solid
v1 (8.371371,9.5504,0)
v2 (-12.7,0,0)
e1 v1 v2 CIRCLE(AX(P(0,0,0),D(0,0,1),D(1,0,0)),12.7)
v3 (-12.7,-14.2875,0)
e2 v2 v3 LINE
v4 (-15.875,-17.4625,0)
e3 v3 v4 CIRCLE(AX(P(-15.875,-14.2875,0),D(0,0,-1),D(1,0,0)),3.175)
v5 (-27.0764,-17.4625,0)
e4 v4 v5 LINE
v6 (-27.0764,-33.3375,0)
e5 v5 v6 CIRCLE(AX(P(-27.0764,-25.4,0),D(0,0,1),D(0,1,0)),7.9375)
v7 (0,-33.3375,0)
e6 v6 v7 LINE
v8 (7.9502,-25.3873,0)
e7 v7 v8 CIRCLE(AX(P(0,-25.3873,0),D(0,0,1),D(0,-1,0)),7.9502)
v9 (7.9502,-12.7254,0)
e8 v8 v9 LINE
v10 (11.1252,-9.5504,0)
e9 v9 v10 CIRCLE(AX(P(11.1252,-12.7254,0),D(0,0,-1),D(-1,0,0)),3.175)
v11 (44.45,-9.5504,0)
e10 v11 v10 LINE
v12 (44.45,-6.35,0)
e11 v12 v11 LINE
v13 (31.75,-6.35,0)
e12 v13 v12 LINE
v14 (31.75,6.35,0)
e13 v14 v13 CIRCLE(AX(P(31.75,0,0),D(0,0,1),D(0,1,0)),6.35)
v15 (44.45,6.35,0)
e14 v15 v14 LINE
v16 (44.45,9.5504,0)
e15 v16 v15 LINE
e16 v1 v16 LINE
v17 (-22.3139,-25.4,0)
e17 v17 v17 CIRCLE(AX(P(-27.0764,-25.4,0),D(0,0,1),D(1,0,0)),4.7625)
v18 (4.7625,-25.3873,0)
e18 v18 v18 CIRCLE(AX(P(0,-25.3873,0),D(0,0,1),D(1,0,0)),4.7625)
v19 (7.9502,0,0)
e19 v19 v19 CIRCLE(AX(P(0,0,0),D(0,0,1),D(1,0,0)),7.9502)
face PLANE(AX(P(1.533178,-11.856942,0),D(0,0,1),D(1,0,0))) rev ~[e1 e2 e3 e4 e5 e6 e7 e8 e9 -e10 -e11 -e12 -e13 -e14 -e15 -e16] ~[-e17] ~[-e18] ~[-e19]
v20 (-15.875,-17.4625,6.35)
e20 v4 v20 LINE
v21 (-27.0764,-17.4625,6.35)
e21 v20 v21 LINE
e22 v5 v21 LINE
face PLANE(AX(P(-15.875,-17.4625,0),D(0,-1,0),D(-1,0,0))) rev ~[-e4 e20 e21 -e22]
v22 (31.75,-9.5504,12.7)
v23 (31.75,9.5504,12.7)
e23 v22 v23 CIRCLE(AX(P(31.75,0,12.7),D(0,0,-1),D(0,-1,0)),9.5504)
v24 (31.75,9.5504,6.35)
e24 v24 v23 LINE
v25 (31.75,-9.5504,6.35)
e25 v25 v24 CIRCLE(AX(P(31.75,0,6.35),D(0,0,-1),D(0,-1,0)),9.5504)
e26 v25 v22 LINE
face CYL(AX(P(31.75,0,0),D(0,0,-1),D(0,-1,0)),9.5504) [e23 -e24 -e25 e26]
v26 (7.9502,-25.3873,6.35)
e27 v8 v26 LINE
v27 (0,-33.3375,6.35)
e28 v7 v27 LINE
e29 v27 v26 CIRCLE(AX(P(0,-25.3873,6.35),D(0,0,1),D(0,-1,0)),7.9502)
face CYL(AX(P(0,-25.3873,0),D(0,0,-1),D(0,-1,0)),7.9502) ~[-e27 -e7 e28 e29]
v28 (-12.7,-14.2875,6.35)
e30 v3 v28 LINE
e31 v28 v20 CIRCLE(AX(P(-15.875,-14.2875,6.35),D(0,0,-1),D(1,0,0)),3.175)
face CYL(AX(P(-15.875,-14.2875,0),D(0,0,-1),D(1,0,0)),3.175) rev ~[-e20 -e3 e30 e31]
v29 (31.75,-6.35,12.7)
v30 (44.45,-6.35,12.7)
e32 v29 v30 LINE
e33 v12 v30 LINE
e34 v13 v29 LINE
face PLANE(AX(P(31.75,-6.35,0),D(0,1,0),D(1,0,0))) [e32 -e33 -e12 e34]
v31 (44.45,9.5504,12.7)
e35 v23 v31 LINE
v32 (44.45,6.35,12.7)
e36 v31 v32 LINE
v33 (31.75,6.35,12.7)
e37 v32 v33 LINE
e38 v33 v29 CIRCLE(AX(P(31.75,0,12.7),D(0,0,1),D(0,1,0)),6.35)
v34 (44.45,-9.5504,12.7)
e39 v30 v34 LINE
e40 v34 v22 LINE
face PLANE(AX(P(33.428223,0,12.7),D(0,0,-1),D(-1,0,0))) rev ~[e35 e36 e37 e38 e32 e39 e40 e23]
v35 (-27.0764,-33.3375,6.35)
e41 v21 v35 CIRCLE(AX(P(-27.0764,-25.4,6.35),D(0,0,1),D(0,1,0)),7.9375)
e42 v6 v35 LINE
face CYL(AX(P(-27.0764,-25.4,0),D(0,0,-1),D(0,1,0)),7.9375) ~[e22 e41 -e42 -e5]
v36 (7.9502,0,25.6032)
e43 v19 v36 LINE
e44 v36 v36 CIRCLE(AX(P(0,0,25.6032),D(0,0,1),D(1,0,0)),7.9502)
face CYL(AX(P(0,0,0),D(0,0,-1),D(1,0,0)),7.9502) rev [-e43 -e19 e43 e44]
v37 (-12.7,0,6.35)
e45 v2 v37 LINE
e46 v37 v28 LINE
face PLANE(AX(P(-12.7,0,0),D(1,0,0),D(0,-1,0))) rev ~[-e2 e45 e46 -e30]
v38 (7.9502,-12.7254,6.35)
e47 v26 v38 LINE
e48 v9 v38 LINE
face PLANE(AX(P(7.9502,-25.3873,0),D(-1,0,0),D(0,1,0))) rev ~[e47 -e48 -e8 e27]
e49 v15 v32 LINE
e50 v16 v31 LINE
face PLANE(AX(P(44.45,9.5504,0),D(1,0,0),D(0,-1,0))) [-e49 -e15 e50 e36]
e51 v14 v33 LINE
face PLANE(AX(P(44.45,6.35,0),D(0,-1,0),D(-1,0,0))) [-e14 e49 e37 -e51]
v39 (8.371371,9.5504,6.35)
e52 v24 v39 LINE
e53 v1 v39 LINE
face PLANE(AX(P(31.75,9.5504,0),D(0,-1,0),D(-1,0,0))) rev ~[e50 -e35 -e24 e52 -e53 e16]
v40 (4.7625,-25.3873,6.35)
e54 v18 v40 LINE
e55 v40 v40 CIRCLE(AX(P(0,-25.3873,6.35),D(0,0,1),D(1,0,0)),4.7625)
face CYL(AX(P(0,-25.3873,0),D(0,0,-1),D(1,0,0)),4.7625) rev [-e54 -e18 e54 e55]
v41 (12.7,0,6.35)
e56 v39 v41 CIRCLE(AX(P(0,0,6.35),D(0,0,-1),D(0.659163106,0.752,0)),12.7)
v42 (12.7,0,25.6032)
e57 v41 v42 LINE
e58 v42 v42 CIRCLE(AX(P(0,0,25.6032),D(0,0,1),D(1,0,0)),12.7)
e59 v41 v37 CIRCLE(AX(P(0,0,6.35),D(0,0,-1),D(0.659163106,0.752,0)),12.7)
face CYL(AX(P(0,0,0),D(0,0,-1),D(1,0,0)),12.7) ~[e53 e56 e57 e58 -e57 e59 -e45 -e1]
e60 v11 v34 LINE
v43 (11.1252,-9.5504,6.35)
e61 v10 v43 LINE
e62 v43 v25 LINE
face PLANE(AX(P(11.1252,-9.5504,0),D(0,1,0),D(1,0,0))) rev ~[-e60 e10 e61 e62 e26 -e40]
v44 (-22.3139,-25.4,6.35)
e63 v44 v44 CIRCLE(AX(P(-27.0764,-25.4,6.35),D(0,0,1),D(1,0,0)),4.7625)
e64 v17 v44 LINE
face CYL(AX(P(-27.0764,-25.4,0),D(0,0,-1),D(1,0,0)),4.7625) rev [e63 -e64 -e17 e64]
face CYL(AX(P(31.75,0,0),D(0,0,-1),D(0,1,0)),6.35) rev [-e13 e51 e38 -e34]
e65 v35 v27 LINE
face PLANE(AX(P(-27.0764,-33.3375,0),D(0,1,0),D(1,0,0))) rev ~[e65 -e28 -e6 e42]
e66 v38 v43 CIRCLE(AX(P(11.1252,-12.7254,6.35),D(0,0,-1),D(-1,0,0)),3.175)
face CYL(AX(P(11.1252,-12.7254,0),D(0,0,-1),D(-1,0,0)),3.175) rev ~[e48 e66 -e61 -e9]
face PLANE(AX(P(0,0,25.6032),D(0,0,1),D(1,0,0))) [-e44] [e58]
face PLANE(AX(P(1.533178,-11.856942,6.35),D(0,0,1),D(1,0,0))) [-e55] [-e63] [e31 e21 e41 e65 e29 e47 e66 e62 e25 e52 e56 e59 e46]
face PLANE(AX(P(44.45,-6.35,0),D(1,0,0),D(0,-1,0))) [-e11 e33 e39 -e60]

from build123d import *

# Parameters (mm, degrees)
HUB_TUBE_SKETCH_R   = 12.7
HUB_TUBE_SKETCH_R_2 = 7.9502
HUB_TUBE_DEPTH      = 25.6032
WEB_BOSS_DEPTH      = 12.7
FORK_EARS_SKETCH_R  = 4.7625
FORK_EARS_DEPTH     = 6.35


with BuildPart() as part:
    # Hub Tube Sketch → Hub Tube (new body)
    with BuildSketch(Plane.XY):
        Circle(HUB_TUBE_SKETCH_R)
        Circle(HUB_TUBE_SKETCH_R_2, mode=Mode.SUBTRACT)
    extrude(amount=HUB_TUBE_DEPTH)



with BuildPart() as body_2:
    # Web Boss Sketch → Web Boss (new body)
    with BuildSketch(Plane.XY):
        with BuildLine():
            Line((31.75, 9.5504), (44.45, 9.5504))
            Line((44.45, 9.5504), (44.45, 6.35))
            Line((44.45, 6.35), (31.75, 6.35))
            ThreePointArc((31.75, 6.35), (25.4, 0), (31.75, -6.35))
            Line((31.75, -6.35), (44.45, -6.35))
            Line((44.45, -6.35), (44.45, -9.5504))
            Line((44.45, -9.5504), (31.75, -9.5504))
            ThreePointArc((31.75, -9.5504), (22.1996, 0), (31.75, 9.5504))
        make_face()
    extrude(amount=WEB_BOSS_DEPTH)


with BuildPart() as part_1:
    add(part.part)

    add(body_2.part)  # Fork Ears merges body 2
    # Fork Ears Sketch → Fork Ears (add)
    with BuildSketch(Plane.XY):
        with BuildLine():
            Line((-12.7, 0), (-12.7, -14.2875))
            ThreePointArc((-12.7, -14.2875), (-13.62993597, -16.53256403), (-15.875, -17.4625))
            Line((-15.875, -17.4625), (-27.0764, -17.4625))
            ThreePointArc((-27.0764, -17.4625), (-35.0139, -25.4), (-27.0764, -33.3375))
            Line((-27.0764, -33.3375), (0, -33.3375))
            ThreePointArc((0, -33.3375), (5.621640332, -31.008940332), (7.9502, -25.3873))
            Line((7.9502, -25.3873), (7.9502, -12.7254))
            ThreePointArc((7.9502, -12.7254), (8.88013597, -10.48033597), (11.1252, -9.5504))
            Line((11.1252, -9.5504), (31.75, -9.5504))
            ThreePointArc((31.75, -9.5504), (22.1996, 0), (31.75, 9.5504))
            Line((31.75, 9.5504), (8.371371443, 9.5504))
            ThreePointArc((8.371371443, 9.5504), (5.242784693, -11.567333689), (-12.7, 0))
        make_face()
        with Locations((-27.0764, -25.4)):
            Circle(FORK_EARS_SKETCH_R, mode=Mode.SUBTRACT)
        with Locations((0, -25.3873)):
            Circle(FORK_EARS_SKETCH_R, mode=Mode.SUBTRACT)
    extrude(amount=FORK_EARS_DEPTH)


solid = part_1.part
